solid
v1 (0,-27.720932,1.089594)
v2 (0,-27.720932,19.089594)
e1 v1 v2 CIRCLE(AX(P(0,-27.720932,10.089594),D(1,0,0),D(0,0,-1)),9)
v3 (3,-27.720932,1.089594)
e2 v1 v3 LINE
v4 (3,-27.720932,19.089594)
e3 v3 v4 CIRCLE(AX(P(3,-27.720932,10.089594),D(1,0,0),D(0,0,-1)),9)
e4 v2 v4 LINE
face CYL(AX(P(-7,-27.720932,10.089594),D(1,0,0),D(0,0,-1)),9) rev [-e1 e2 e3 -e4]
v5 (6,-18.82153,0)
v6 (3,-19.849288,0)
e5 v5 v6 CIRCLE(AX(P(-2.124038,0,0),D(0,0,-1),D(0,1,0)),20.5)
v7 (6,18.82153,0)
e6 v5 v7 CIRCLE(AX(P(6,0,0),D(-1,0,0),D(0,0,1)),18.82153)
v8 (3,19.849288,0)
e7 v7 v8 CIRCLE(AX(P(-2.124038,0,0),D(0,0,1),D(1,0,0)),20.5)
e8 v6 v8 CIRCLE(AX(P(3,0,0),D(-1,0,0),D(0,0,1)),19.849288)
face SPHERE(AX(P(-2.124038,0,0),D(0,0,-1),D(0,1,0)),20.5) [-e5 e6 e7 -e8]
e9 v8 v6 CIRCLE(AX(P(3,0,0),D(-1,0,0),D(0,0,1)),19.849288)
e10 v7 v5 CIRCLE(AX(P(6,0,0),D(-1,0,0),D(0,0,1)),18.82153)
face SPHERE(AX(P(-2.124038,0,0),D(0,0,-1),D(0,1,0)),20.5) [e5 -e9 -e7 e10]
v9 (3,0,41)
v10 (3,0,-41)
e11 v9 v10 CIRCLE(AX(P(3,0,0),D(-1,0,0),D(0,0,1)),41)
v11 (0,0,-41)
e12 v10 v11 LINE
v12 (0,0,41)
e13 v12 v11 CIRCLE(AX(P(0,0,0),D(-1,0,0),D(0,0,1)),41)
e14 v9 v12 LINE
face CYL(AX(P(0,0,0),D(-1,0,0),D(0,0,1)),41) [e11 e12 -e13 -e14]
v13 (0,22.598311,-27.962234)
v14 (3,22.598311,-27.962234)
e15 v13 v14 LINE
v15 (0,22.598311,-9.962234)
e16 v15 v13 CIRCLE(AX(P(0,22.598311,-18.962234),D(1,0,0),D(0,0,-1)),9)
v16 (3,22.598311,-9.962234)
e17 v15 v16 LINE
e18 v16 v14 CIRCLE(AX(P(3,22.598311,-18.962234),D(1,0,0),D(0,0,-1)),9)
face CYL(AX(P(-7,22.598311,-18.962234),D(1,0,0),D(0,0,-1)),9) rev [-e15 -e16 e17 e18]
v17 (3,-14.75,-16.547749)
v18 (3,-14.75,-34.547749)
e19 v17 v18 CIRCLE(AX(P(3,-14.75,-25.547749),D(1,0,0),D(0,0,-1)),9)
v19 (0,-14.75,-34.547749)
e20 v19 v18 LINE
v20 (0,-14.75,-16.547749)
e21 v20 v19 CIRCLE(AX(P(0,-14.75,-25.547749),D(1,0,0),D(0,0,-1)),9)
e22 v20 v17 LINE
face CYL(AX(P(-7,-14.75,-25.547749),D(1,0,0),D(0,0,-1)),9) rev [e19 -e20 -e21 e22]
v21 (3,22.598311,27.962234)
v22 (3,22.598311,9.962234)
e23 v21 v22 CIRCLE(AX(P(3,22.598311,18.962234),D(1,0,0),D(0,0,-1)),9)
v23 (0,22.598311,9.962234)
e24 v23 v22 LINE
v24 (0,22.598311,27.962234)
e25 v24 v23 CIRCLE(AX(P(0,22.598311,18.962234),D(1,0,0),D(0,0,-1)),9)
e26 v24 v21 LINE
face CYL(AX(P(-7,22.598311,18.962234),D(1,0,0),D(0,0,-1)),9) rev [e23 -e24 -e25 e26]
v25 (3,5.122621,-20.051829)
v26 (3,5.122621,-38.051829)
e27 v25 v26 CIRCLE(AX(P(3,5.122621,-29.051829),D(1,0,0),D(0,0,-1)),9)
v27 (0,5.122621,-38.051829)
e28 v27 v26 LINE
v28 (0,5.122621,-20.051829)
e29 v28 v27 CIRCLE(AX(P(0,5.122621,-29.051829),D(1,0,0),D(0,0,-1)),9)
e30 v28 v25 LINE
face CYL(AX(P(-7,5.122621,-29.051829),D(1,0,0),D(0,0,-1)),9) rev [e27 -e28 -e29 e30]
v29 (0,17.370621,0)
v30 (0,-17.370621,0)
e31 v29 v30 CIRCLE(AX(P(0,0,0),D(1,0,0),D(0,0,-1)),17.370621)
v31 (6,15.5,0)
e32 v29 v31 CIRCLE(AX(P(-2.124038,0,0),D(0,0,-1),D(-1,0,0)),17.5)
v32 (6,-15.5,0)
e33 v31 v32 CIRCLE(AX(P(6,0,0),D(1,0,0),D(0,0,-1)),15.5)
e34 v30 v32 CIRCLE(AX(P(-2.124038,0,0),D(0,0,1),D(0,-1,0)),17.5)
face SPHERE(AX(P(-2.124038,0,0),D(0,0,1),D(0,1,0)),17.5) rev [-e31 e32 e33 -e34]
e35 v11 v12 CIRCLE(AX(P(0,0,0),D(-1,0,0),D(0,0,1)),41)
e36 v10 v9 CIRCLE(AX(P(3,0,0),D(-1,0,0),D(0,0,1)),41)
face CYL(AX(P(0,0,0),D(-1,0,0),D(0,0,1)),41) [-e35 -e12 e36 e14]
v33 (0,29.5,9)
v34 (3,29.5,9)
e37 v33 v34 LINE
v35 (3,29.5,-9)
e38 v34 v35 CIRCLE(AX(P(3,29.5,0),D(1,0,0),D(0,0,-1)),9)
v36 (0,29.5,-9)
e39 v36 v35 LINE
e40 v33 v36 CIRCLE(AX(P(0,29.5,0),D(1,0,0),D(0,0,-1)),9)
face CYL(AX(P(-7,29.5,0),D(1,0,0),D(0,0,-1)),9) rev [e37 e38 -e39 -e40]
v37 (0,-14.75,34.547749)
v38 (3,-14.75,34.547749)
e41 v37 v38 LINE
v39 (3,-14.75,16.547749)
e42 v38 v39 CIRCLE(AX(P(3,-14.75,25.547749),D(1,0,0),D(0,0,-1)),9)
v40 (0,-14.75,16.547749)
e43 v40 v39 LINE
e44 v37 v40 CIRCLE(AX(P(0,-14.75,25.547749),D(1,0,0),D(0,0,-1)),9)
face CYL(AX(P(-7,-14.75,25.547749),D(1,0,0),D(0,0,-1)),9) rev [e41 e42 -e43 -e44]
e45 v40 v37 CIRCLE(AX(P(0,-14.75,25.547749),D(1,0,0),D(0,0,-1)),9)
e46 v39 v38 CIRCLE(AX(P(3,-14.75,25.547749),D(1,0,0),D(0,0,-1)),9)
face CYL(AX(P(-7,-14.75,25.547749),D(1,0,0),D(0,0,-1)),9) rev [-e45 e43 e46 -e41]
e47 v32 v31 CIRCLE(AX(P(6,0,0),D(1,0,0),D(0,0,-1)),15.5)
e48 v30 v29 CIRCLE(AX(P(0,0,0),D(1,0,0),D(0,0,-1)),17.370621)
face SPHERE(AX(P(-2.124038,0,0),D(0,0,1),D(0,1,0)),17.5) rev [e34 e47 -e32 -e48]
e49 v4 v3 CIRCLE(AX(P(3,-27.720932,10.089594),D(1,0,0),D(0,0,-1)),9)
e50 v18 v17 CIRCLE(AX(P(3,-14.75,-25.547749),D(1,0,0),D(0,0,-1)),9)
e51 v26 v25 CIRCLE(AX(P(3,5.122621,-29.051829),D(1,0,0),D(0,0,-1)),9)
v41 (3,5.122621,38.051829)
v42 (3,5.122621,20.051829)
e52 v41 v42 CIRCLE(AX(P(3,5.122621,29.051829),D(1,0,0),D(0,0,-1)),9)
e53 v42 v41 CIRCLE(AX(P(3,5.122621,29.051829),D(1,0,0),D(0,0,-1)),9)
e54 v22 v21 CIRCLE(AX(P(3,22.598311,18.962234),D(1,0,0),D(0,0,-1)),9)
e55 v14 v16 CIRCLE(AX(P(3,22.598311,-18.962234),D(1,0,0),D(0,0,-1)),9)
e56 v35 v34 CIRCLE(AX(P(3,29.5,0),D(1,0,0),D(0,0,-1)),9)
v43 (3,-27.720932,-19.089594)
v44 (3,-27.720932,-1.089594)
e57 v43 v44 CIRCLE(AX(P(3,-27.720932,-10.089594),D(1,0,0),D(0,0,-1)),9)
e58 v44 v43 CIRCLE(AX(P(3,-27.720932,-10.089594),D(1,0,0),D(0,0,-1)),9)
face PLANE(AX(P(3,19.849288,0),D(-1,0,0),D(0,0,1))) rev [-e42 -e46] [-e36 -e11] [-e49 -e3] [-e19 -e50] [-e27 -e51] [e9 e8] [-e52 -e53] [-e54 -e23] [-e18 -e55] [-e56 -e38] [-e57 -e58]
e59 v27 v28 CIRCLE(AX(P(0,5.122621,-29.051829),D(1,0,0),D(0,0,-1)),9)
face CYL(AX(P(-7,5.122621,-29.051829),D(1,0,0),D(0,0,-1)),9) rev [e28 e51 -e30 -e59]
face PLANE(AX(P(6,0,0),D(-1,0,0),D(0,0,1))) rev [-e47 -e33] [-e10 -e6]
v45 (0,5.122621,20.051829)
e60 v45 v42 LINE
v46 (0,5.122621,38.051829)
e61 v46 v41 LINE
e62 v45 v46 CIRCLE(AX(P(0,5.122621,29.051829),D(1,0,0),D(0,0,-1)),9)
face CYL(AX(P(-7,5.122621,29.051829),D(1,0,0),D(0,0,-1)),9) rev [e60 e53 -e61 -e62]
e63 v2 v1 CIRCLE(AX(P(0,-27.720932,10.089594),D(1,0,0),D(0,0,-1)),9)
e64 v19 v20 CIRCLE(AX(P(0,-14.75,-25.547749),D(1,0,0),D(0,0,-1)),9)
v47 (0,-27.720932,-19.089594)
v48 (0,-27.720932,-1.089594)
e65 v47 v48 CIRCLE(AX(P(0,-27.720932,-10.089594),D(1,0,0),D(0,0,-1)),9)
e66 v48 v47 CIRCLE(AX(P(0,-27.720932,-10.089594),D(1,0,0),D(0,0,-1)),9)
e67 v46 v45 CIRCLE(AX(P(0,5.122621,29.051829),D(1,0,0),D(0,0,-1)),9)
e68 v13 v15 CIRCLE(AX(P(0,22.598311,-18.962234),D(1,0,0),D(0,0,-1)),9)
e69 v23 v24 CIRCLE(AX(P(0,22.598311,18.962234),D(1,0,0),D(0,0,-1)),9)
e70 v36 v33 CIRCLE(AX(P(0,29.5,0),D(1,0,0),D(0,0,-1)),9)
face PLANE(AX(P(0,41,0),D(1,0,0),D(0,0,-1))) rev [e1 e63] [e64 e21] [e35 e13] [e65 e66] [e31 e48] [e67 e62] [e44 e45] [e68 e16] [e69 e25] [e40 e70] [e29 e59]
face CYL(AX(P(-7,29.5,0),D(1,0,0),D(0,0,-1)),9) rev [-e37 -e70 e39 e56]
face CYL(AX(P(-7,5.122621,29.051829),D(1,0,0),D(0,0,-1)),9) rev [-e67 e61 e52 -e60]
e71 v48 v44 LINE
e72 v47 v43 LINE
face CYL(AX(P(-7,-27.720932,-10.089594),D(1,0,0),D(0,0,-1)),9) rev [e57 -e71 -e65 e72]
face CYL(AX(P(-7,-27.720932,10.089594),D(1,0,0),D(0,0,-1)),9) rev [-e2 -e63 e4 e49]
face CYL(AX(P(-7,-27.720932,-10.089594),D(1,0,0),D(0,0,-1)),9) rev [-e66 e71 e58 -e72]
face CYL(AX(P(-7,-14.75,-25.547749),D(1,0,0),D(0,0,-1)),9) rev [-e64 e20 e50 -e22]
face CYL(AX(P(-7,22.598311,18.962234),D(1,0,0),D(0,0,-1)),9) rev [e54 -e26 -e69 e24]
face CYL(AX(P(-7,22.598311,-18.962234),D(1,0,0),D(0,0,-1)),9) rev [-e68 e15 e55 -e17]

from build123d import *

# Parameters (mm, degrees)
SKETCH4_R          = 9
CUT_EXTRUDE1_DEPTH = 10


with BuildPart() as part:
    # Sketch2 → Revolve1 (revolve)
    with BuildSketch(Plane.XY):
        with BuildLine():
            Line((6, 0), (6, 18.821530225))
            ThreePointArc((6, 18.821530225), (4.519902914, 19.393505195), (3, 19.849287907))
            Line((3, 19.849287907), (3, 41))
            Line((3, 41), (0, 41))
            Line((0, 41), (0, 0))
            Line((0, 0), (6, 0))
        make_face()
    revolve(axis=Axis((0, 0, 0), (1, 0, 0)))

    # Sketch3 → Cut-Revolve1 (revolve, cut)
    with BuildSketch(Plane.XY, mode=Mode.PRIVATE) as cut_revolve1_sk:
        with BuildLine():
            Line((6, 15.5), (6, 0))
            Line((6, 0), (0, 0))
            Line((0, 0), (0, 17.370620624))
            ThreePointArc((0, 17.370620624), (3.084663444, 16.706867601), (6, 15.5))
        make_face()
    revolve(cut_revolve1_sk.sketch.rotate(Axis((6, 0, 0), (-1, 0, 0)), 270), axis=Axis((6, 0, 0), (-1, 0, 0)), mode=Mode.SUBTRACT)

    # Sketch4 → Cut-Extrude1 (cut)
    with BuildSketch(Plane(origin=(3, 0, 0), x_dir=(0, 0, -1), z_dir=(1, 0, 0))):
        with Locations((0, 29.5)):
            Circle(SKETCH4_R)
        with Locations((18.962234486, 22.598311072)):
            Circle(SKETCH4_R)
        with Locations((29.051828714, 5.122621241)):
            Circle(SKETCH4_R)
        with Locations((25.547749412, -14.75)):
            Circle(SKETCH4_R)
        with Locations((10.089594228, -27.720932313)):
            Circle(SKETCH4_R)
        with Locations((-10.089594228, -27.720932313)):
            Circle(SKETCH4_R)
        with Locations((-25.547749412, -14.75)):
            Circle(SKETCH4_R)
        with Locations((-29.051828714, 5.122621241)):
            Circle(SKETCH4_R)
        with Locations((-18.962234486, 22.598311072)):
            Circle(SKETCH4_R)
    extrude(amount=-CUT_EXTRUDE1_DEPTH, mode=Mode.SUBTRACT)


solid = part.part
